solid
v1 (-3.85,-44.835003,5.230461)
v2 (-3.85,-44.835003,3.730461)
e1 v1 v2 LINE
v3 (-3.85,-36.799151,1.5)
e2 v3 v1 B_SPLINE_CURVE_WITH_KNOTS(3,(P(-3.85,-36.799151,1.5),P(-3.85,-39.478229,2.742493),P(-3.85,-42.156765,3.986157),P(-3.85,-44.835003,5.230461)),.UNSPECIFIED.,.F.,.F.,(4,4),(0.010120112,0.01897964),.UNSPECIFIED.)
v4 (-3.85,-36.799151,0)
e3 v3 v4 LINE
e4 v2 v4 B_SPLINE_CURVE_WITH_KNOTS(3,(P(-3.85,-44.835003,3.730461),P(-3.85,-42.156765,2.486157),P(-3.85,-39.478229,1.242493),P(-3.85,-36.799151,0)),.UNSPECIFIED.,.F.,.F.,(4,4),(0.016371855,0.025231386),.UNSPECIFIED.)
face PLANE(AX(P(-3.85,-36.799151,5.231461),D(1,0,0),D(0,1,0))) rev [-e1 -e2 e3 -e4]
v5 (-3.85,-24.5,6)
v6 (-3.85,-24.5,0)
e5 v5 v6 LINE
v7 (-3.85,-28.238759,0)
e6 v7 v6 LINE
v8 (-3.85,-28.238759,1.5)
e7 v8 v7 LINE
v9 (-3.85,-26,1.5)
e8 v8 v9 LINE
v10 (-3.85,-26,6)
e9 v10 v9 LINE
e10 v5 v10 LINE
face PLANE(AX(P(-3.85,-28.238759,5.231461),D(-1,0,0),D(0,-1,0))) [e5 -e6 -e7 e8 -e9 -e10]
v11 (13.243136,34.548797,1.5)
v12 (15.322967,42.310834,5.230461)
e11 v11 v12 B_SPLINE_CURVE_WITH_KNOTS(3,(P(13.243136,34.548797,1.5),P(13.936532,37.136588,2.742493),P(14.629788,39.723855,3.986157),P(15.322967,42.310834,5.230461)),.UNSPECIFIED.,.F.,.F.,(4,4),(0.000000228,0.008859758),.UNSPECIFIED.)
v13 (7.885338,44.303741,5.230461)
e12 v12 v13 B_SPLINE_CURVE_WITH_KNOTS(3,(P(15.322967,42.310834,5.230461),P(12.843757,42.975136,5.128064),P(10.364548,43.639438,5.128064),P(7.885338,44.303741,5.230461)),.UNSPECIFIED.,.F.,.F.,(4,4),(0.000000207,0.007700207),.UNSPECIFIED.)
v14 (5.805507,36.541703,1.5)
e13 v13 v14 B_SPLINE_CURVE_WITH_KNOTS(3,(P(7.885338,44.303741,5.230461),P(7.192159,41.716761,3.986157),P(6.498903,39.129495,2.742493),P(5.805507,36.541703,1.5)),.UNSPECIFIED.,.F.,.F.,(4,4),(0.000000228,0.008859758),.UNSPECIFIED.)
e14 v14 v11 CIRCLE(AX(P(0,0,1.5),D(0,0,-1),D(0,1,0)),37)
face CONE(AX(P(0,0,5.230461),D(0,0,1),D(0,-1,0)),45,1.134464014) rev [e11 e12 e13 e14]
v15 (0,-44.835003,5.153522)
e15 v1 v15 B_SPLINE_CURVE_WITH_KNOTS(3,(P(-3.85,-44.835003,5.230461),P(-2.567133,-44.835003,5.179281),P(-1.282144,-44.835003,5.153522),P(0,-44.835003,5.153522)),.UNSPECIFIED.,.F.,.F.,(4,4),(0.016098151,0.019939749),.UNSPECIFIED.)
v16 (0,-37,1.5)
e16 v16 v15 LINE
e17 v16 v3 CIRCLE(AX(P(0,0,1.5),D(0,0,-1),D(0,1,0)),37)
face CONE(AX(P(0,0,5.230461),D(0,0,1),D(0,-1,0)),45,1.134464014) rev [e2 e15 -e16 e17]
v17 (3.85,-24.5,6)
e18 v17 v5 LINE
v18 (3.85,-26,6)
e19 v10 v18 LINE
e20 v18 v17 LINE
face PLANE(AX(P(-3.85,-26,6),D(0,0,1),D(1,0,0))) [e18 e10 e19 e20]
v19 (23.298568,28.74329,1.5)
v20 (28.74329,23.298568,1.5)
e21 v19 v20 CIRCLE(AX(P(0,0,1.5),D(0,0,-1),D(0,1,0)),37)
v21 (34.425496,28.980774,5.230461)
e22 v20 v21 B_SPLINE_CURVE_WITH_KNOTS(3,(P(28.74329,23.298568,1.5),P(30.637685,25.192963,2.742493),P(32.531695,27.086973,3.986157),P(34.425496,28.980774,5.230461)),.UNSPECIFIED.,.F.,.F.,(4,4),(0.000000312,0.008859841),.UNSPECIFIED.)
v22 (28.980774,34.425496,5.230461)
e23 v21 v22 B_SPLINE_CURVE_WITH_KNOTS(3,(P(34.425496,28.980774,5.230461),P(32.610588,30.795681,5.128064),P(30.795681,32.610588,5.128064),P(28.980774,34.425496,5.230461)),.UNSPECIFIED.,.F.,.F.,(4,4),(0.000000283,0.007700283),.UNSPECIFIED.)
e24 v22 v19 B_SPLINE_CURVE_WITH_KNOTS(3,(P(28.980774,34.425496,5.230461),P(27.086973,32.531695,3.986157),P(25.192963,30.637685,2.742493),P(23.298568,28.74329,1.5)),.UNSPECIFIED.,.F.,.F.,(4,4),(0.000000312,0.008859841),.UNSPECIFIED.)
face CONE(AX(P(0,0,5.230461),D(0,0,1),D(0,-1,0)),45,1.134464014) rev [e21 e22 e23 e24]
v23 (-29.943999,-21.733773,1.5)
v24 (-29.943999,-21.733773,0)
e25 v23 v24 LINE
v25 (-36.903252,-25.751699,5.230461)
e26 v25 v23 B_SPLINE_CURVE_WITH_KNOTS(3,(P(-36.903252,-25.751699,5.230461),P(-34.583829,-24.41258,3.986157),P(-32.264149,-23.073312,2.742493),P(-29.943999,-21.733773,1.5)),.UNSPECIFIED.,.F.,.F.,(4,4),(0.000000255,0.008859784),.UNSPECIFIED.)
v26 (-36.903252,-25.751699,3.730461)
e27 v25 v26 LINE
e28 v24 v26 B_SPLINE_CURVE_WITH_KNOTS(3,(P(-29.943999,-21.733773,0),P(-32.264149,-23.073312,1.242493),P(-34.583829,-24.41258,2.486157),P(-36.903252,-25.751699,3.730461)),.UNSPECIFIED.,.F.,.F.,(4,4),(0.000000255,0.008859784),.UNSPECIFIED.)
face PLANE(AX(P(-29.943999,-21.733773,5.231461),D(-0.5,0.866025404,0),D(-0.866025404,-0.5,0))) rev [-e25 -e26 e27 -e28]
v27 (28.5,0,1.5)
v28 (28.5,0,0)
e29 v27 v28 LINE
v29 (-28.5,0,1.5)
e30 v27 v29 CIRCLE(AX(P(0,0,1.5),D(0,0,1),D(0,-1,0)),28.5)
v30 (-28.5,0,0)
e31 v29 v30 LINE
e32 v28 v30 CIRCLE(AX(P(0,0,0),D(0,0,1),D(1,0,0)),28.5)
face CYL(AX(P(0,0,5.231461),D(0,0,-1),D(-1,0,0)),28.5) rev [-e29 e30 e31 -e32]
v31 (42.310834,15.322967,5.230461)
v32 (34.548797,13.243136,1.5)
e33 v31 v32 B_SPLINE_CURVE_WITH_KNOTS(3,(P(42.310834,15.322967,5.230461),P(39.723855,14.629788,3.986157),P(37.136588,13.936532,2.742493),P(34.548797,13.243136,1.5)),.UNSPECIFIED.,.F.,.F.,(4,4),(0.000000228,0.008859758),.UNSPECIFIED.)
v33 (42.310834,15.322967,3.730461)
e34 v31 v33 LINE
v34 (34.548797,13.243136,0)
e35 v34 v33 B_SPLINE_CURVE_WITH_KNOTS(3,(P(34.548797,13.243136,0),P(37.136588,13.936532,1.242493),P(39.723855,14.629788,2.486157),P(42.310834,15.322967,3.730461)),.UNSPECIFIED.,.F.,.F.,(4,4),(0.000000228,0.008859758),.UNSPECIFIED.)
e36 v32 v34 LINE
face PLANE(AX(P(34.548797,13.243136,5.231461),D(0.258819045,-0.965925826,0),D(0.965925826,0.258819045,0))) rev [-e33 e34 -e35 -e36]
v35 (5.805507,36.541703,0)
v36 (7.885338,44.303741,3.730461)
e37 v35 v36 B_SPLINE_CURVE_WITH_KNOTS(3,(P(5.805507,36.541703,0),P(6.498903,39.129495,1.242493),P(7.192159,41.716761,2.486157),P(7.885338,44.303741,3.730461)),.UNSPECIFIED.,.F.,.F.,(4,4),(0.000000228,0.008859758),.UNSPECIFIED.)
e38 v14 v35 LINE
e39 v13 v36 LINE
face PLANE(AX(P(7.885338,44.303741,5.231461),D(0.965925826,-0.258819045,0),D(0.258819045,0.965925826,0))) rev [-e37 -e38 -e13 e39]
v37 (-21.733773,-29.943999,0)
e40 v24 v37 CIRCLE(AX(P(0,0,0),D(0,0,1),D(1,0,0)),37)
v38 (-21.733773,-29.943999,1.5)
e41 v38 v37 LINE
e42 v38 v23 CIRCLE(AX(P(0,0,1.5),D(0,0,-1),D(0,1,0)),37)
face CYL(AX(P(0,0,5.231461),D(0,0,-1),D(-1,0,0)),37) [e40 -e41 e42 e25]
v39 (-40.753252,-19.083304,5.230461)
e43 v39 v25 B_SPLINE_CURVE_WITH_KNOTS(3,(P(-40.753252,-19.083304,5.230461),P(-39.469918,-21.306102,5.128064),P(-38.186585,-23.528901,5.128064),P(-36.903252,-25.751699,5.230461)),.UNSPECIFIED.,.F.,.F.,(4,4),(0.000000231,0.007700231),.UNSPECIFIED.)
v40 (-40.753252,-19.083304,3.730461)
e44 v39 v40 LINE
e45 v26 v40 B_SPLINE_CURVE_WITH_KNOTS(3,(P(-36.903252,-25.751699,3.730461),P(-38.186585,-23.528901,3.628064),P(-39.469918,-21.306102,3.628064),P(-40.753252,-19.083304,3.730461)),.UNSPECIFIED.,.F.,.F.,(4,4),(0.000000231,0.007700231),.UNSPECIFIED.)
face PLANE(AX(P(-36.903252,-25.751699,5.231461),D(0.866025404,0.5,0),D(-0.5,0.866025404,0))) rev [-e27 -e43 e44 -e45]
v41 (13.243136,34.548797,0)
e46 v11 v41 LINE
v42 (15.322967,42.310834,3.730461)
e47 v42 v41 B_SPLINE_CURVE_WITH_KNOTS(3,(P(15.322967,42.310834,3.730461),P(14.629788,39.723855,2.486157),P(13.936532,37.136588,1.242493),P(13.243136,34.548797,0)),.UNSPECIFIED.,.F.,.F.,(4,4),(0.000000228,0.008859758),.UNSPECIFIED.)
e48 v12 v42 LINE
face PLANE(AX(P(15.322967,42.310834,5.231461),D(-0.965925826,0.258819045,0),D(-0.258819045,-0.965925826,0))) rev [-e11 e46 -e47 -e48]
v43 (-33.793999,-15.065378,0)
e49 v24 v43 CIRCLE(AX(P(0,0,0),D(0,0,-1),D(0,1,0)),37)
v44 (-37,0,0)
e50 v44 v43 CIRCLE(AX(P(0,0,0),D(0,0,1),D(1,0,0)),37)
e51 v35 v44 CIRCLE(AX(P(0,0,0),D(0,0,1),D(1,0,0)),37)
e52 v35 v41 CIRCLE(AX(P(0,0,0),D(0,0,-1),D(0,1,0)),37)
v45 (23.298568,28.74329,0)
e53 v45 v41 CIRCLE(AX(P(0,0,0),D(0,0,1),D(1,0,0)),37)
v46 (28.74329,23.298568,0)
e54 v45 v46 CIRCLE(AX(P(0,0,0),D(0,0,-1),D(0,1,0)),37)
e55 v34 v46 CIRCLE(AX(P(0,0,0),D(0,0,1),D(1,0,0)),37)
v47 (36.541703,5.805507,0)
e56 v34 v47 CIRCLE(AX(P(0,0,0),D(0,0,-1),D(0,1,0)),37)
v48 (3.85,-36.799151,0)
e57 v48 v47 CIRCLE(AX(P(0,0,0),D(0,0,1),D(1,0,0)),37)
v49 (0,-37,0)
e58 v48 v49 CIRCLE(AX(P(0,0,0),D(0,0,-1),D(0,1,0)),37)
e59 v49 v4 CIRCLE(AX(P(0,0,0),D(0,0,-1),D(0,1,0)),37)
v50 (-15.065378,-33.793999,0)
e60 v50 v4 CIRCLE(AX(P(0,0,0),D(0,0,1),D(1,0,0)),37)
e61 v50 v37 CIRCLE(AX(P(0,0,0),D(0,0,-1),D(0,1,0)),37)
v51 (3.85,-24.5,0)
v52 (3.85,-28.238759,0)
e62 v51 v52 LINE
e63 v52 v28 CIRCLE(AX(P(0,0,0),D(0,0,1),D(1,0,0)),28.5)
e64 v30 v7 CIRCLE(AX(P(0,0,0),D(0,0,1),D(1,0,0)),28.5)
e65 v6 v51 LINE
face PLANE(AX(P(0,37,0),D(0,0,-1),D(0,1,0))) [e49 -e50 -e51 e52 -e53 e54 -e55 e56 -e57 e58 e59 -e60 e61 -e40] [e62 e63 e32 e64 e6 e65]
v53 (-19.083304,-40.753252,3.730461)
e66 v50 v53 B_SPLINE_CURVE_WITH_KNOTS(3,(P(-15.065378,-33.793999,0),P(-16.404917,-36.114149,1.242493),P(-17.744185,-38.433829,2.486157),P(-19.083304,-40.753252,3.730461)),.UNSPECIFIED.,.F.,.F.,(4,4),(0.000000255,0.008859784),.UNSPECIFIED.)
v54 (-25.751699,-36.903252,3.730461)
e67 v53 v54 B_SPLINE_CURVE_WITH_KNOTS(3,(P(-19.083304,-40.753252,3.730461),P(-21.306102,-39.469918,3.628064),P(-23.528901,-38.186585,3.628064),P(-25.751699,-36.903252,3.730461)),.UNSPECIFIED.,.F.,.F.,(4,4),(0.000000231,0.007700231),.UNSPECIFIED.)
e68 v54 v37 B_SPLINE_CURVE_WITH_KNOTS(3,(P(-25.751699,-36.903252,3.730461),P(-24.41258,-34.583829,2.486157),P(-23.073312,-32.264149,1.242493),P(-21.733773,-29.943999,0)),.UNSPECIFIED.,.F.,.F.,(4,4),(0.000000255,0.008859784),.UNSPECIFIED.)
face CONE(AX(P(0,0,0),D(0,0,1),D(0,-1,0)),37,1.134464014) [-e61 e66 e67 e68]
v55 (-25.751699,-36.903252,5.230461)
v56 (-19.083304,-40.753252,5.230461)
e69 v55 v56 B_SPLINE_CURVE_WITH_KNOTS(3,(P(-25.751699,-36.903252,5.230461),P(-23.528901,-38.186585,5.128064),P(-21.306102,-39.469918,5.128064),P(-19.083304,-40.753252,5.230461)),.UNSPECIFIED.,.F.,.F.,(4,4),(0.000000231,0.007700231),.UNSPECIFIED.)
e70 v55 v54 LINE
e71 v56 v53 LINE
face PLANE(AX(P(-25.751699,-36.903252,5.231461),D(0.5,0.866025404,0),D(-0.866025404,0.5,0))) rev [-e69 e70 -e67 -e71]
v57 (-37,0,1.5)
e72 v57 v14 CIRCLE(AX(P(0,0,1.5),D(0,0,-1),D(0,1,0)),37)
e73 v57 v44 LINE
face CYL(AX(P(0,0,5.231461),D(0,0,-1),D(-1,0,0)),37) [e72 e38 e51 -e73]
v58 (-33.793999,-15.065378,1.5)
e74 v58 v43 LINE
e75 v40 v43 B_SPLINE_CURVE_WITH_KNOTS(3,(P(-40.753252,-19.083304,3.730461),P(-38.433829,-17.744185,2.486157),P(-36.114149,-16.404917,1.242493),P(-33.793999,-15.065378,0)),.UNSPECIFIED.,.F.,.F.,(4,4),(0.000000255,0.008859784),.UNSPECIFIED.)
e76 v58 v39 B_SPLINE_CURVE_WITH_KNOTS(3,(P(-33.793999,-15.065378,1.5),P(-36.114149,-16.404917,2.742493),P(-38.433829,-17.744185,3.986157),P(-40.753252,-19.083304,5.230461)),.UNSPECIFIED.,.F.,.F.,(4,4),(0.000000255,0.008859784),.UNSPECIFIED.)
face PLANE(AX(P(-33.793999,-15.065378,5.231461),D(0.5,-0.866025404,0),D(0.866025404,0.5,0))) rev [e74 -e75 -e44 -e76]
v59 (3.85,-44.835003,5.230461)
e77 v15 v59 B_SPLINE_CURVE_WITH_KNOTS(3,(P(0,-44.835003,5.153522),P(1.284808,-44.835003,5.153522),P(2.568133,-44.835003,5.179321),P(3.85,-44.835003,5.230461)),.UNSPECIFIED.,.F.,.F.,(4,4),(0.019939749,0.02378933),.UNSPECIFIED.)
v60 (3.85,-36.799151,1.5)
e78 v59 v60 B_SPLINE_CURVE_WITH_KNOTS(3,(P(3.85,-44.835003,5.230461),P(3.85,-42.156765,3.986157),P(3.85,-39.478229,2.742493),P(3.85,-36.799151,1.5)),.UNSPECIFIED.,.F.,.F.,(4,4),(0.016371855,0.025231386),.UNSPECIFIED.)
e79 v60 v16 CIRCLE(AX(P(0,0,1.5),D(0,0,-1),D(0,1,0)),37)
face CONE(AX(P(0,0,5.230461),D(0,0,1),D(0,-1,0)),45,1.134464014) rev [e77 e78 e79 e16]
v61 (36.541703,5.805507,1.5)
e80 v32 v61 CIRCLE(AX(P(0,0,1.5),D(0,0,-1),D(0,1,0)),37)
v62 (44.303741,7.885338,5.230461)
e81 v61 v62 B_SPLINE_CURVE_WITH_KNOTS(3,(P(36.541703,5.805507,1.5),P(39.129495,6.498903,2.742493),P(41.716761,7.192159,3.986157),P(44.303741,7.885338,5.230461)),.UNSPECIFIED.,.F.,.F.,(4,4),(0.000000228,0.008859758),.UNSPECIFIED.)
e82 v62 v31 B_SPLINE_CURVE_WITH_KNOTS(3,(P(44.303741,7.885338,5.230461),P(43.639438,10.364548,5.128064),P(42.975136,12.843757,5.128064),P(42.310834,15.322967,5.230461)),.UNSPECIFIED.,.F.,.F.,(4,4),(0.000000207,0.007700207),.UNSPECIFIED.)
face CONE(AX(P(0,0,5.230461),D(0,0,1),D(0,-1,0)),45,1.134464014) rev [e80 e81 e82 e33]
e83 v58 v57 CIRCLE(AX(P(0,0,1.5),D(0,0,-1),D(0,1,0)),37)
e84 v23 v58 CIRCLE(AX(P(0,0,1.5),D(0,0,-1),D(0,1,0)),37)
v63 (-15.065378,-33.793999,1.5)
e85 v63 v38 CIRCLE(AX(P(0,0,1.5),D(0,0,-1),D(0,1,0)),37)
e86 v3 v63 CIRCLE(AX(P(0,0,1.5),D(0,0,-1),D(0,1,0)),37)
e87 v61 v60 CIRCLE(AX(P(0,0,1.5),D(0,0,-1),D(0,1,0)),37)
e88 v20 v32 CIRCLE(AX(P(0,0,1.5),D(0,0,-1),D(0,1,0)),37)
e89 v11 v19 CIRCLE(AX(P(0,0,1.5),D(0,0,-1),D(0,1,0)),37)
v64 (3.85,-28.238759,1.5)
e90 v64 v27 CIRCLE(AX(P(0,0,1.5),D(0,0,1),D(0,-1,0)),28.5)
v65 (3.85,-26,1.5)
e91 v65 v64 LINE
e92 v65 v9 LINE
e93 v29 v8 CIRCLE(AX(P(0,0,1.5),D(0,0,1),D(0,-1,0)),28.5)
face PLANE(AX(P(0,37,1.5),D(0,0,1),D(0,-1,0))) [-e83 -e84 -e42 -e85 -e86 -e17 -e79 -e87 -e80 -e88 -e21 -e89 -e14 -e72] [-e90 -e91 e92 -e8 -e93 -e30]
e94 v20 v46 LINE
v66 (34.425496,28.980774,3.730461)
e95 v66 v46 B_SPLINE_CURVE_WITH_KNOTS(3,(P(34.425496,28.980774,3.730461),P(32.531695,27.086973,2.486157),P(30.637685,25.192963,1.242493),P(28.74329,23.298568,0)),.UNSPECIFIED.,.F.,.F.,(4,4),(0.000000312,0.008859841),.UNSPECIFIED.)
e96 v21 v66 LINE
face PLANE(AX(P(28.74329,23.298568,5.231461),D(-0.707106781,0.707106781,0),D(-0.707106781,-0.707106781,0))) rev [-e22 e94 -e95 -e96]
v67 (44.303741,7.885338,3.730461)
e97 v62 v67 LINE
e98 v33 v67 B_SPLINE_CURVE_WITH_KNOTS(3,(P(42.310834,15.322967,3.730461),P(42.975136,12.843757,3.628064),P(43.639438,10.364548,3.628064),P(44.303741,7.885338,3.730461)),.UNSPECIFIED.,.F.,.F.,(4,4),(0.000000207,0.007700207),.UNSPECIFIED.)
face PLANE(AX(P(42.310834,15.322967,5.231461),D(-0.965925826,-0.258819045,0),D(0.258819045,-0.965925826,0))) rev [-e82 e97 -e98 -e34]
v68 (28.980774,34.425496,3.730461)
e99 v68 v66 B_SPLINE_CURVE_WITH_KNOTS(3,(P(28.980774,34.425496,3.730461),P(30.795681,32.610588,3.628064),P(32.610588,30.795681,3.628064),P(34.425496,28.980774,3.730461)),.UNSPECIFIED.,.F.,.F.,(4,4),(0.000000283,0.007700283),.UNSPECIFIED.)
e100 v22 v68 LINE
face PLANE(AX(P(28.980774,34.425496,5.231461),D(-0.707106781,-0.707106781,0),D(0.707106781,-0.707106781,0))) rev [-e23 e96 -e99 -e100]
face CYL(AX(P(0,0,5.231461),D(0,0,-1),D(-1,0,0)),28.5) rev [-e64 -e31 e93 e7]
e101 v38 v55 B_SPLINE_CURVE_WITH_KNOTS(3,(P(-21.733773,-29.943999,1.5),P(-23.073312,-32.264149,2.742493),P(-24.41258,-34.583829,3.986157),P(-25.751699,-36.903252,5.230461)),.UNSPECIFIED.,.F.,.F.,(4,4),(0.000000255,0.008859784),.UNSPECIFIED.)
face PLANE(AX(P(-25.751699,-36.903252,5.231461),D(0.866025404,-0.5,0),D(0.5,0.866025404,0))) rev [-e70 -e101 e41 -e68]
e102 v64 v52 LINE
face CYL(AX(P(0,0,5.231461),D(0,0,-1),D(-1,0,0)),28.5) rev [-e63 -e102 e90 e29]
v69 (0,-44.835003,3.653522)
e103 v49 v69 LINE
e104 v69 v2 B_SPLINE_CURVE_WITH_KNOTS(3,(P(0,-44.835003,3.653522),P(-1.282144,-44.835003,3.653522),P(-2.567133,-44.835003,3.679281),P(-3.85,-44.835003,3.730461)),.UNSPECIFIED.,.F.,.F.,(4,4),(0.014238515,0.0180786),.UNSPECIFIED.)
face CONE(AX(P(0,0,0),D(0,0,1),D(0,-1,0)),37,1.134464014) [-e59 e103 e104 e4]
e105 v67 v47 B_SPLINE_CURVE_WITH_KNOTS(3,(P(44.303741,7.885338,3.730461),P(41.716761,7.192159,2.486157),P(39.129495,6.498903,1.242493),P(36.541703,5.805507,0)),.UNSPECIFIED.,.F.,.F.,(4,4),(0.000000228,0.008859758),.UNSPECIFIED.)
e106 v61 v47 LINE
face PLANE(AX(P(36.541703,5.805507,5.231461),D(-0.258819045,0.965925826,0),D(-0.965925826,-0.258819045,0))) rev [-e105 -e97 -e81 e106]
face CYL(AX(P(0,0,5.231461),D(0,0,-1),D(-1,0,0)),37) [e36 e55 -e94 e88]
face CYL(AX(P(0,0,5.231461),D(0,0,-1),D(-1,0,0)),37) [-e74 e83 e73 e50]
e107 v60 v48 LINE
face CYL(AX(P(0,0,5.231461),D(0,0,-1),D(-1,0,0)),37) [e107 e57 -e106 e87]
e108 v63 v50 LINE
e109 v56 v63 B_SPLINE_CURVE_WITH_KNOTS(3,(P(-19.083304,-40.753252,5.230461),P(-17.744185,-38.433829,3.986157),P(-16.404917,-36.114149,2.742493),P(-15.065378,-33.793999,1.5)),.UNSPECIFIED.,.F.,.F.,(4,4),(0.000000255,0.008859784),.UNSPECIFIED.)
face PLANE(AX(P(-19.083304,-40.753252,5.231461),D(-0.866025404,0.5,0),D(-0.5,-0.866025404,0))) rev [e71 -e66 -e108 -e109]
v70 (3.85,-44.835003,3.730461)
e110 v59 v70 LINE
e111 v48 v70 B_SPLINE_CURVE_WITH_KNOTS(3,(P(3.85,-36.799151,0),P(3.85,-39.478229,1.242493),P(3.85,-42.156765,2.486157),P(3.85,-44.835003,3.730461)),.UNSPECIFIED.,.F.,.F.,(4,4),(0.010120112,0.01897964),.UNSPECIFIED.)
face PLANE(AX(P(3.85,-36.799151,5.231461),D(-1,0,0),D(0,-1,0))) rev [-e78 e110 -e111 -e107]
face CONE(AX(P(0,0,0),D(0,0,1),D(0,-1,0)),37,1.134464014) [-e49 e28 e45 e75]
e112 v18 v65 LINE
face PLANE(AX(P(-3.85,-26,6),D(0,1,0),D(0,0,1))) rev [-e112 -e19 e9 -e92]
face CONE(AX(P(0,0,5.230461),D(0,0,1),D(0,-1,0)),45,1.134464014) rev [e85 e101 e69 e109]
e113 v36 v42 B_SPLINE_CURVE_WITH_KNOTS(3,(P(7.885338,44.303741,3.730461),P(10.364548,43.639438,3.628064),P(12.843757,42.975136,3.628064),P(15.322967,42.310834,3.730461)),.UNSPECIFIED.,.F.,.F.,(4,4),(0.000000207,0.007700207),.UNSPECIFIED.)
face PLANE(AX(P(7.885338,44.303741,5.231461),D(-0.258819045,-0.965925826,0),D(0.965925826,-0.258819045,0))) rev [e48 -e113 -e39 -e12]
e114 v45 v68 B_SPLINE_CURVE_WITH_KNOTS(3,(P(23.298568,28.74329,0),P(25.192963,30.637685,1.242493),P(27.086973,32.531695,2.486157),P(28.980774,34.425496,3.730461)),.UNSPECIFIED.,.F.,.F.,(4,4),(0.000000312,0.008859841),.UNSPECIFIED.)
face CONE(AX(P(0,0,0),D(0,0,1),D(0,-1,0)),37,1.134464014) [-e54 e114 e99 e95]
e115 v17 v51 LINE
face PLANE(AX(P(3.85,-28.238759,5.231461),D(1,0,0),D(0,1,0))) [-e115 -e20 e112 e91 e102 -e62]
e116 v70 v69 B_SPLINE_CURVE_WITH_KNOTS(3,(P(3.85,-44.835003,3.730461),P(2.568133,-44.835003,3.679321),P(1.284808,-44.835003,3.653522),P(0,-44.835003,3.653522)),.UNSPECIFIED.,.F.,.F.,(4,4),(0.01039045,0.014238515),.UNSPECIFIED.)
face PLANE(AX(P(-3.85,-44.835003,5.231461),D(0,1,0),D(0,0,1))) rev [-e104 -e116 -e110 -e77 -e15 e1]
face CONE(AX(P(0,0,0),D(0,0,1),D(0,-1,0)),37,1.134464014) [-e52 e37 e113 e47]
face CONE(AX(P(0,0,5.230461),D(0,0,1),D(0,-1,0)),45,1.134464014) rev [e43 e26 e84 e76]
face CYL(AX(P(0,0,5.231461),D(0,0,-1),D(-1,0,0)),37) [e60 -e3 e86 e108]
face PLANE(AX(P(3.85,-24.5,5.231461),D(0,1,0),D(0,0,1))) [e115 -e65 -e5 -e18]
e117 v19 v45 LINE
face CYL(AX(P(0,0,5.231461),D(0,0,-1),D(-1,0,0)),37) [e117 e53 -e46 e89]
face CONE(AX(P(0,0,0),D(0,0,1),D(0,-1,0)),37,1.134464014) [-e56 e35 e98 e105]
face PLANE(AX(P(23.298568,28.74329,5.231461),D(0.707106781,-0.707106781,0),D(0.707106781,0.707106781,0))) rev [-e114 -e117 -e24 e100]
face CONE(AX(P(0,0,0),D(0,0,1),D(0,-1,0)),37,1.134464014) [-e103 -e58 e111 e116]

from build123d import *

# Parameters (mm, degrees)
SKETCH3_OUTSIDE_W   = 117.478
SKETCH3_OUTSIDE_H   = 117.478
CUT_EXTRUDE2_DEPTH  = 5.230463
SKETCH4_W           = 7.7
SKETCH4_H           = 1.5
BOSS_EXTRUDE1_DEPTH = 6


with BuildPart() as part:
    # Sketch2 → Base-Revolve (revolve)
    with BuildSketch(Plane(origin=(0, 0, 0), x_dir=(0, 0, -1), z_dir=(1, 0, 0))):
        Polygon((-3.730461265, 45), (0, 37), (0, 0), (-1.5, 0), (-1.5, 37), (-5.230461265, 45), align=None)
    revolve(axis=Axis((0, 0, 0), (0, 0, 1)))

    # Sketch3 outside → Cut-Extrude2 (cut)
    # profile 1 of 2: a face of its own
    with BuildSketch(Plane.XY):
        Rectangle(SKETCH3_OUTSIDE_W, SKETCH3_OUTSIDE_H)
        with BuildLine():
            Line((-3.85, -36.799150805), (-3.85, -44.835003067))
            Line((-3.85, -44.835003067), (3.85, -44.835003067))
            Line((3.85, -44.835003067), (3.85, -36.799150805))
            ThreePointArc((3.85, -36.799150805), (29.354073591, -22.524172873), (36.541703472, 5.805506641))
            Line((36.541703472, 5.805506641), (44.303740708, 7.88533825))
            Line((44.303740708, 7.88533825), (42.31083406, 15.322967112))
            Line((42.31083406, 15.322967112), (34.548796825, 13.243135503))
            ThreePointArc((34.548796825, 13.243135503), (32.04293994, 18.5), (28.743290184, 23.298567969))
            Line((28.743290184, 23.298567969), (34.425495811, 28.980773595))
            Line((34.425495811, 28.980773595), (28.980773595, 34.425495811))
            Line((28.980773595, 34.425495811), (23.298567969, 28.743290184))
            ThreePointArc((23.298567969, 28.743290184), (18.5, 32.04293994), (13.243135503, 34.548796825))
            Line((13.243135503, 34.548796825), (15.322967112, 42.31083406))
            Line((15.322967112, 42.31083406), (7.88533825, 44.303740708))
            Line((7.88533825, 44.303740708), (5.805506641, 36.541703472))
            ThreePointArc((5.805506641, 36.541703472), (-29.354073591, 22.524172873), (-33.793999435, -15.065377598))
            Line((-33.793999435, -15.065377598), (-40.753251635, -19.083303729))
            Line((-40.753251635, -19.083303729), (-36.903251635, -25.751699338))
            Line((-36.903251635, -25.751699338), (-29.943999435, -21.733773207))
            ThreePointArc((-29.943999435, -21.733773207), (-26.162950904, -26.162950904), (-21.733773207, -29.943999435))
            Line((-21.733773207, -29.943999435), (-25.751699338, -36.903251635))
            Line((-25.751699338, -36.903251635), (-19.083303729, -40.753251635))
            Line((-19.083303729, -40.753251635), (-15.065377598, -33.793999435))
            ThreePointArc((-15.065377598, -33.793999435), (-9.576304669, -35.739255573), (-3.85, -36.799150805))
        make_face(mode=Mode.SUBTRACT)
    # profile 2 of 2: a face of its own
    with BuildSketch(Plane.XY):
        with BuildLine():
            Line((3.85, -28.238758825), (3.85, -24.5))
            Line((3.85, -24.5), (-3.85, -24.5))
            Line((-3.85, -24.5), (-3.85, -28.238758825))
            ThreePointArc((-3.85, -28.238758825), (0, 28.5), (3.85, -28.238758825))
        make_face()
    extrude(amount=CUT_EXTRUDE2_DEPTH, mode=Mode.SUBTRACT)

    # Sketch4 → Boss-Extrude1 (add)
    with BuildSketch(Plane.XY):
        with Locations((0, -25.25)):
            Rectangle(SKETCH4_W, SKETCH4_H)
    extrude(amount=BOSS_EXTRUDE1_DEPTH)


solid = part.part
